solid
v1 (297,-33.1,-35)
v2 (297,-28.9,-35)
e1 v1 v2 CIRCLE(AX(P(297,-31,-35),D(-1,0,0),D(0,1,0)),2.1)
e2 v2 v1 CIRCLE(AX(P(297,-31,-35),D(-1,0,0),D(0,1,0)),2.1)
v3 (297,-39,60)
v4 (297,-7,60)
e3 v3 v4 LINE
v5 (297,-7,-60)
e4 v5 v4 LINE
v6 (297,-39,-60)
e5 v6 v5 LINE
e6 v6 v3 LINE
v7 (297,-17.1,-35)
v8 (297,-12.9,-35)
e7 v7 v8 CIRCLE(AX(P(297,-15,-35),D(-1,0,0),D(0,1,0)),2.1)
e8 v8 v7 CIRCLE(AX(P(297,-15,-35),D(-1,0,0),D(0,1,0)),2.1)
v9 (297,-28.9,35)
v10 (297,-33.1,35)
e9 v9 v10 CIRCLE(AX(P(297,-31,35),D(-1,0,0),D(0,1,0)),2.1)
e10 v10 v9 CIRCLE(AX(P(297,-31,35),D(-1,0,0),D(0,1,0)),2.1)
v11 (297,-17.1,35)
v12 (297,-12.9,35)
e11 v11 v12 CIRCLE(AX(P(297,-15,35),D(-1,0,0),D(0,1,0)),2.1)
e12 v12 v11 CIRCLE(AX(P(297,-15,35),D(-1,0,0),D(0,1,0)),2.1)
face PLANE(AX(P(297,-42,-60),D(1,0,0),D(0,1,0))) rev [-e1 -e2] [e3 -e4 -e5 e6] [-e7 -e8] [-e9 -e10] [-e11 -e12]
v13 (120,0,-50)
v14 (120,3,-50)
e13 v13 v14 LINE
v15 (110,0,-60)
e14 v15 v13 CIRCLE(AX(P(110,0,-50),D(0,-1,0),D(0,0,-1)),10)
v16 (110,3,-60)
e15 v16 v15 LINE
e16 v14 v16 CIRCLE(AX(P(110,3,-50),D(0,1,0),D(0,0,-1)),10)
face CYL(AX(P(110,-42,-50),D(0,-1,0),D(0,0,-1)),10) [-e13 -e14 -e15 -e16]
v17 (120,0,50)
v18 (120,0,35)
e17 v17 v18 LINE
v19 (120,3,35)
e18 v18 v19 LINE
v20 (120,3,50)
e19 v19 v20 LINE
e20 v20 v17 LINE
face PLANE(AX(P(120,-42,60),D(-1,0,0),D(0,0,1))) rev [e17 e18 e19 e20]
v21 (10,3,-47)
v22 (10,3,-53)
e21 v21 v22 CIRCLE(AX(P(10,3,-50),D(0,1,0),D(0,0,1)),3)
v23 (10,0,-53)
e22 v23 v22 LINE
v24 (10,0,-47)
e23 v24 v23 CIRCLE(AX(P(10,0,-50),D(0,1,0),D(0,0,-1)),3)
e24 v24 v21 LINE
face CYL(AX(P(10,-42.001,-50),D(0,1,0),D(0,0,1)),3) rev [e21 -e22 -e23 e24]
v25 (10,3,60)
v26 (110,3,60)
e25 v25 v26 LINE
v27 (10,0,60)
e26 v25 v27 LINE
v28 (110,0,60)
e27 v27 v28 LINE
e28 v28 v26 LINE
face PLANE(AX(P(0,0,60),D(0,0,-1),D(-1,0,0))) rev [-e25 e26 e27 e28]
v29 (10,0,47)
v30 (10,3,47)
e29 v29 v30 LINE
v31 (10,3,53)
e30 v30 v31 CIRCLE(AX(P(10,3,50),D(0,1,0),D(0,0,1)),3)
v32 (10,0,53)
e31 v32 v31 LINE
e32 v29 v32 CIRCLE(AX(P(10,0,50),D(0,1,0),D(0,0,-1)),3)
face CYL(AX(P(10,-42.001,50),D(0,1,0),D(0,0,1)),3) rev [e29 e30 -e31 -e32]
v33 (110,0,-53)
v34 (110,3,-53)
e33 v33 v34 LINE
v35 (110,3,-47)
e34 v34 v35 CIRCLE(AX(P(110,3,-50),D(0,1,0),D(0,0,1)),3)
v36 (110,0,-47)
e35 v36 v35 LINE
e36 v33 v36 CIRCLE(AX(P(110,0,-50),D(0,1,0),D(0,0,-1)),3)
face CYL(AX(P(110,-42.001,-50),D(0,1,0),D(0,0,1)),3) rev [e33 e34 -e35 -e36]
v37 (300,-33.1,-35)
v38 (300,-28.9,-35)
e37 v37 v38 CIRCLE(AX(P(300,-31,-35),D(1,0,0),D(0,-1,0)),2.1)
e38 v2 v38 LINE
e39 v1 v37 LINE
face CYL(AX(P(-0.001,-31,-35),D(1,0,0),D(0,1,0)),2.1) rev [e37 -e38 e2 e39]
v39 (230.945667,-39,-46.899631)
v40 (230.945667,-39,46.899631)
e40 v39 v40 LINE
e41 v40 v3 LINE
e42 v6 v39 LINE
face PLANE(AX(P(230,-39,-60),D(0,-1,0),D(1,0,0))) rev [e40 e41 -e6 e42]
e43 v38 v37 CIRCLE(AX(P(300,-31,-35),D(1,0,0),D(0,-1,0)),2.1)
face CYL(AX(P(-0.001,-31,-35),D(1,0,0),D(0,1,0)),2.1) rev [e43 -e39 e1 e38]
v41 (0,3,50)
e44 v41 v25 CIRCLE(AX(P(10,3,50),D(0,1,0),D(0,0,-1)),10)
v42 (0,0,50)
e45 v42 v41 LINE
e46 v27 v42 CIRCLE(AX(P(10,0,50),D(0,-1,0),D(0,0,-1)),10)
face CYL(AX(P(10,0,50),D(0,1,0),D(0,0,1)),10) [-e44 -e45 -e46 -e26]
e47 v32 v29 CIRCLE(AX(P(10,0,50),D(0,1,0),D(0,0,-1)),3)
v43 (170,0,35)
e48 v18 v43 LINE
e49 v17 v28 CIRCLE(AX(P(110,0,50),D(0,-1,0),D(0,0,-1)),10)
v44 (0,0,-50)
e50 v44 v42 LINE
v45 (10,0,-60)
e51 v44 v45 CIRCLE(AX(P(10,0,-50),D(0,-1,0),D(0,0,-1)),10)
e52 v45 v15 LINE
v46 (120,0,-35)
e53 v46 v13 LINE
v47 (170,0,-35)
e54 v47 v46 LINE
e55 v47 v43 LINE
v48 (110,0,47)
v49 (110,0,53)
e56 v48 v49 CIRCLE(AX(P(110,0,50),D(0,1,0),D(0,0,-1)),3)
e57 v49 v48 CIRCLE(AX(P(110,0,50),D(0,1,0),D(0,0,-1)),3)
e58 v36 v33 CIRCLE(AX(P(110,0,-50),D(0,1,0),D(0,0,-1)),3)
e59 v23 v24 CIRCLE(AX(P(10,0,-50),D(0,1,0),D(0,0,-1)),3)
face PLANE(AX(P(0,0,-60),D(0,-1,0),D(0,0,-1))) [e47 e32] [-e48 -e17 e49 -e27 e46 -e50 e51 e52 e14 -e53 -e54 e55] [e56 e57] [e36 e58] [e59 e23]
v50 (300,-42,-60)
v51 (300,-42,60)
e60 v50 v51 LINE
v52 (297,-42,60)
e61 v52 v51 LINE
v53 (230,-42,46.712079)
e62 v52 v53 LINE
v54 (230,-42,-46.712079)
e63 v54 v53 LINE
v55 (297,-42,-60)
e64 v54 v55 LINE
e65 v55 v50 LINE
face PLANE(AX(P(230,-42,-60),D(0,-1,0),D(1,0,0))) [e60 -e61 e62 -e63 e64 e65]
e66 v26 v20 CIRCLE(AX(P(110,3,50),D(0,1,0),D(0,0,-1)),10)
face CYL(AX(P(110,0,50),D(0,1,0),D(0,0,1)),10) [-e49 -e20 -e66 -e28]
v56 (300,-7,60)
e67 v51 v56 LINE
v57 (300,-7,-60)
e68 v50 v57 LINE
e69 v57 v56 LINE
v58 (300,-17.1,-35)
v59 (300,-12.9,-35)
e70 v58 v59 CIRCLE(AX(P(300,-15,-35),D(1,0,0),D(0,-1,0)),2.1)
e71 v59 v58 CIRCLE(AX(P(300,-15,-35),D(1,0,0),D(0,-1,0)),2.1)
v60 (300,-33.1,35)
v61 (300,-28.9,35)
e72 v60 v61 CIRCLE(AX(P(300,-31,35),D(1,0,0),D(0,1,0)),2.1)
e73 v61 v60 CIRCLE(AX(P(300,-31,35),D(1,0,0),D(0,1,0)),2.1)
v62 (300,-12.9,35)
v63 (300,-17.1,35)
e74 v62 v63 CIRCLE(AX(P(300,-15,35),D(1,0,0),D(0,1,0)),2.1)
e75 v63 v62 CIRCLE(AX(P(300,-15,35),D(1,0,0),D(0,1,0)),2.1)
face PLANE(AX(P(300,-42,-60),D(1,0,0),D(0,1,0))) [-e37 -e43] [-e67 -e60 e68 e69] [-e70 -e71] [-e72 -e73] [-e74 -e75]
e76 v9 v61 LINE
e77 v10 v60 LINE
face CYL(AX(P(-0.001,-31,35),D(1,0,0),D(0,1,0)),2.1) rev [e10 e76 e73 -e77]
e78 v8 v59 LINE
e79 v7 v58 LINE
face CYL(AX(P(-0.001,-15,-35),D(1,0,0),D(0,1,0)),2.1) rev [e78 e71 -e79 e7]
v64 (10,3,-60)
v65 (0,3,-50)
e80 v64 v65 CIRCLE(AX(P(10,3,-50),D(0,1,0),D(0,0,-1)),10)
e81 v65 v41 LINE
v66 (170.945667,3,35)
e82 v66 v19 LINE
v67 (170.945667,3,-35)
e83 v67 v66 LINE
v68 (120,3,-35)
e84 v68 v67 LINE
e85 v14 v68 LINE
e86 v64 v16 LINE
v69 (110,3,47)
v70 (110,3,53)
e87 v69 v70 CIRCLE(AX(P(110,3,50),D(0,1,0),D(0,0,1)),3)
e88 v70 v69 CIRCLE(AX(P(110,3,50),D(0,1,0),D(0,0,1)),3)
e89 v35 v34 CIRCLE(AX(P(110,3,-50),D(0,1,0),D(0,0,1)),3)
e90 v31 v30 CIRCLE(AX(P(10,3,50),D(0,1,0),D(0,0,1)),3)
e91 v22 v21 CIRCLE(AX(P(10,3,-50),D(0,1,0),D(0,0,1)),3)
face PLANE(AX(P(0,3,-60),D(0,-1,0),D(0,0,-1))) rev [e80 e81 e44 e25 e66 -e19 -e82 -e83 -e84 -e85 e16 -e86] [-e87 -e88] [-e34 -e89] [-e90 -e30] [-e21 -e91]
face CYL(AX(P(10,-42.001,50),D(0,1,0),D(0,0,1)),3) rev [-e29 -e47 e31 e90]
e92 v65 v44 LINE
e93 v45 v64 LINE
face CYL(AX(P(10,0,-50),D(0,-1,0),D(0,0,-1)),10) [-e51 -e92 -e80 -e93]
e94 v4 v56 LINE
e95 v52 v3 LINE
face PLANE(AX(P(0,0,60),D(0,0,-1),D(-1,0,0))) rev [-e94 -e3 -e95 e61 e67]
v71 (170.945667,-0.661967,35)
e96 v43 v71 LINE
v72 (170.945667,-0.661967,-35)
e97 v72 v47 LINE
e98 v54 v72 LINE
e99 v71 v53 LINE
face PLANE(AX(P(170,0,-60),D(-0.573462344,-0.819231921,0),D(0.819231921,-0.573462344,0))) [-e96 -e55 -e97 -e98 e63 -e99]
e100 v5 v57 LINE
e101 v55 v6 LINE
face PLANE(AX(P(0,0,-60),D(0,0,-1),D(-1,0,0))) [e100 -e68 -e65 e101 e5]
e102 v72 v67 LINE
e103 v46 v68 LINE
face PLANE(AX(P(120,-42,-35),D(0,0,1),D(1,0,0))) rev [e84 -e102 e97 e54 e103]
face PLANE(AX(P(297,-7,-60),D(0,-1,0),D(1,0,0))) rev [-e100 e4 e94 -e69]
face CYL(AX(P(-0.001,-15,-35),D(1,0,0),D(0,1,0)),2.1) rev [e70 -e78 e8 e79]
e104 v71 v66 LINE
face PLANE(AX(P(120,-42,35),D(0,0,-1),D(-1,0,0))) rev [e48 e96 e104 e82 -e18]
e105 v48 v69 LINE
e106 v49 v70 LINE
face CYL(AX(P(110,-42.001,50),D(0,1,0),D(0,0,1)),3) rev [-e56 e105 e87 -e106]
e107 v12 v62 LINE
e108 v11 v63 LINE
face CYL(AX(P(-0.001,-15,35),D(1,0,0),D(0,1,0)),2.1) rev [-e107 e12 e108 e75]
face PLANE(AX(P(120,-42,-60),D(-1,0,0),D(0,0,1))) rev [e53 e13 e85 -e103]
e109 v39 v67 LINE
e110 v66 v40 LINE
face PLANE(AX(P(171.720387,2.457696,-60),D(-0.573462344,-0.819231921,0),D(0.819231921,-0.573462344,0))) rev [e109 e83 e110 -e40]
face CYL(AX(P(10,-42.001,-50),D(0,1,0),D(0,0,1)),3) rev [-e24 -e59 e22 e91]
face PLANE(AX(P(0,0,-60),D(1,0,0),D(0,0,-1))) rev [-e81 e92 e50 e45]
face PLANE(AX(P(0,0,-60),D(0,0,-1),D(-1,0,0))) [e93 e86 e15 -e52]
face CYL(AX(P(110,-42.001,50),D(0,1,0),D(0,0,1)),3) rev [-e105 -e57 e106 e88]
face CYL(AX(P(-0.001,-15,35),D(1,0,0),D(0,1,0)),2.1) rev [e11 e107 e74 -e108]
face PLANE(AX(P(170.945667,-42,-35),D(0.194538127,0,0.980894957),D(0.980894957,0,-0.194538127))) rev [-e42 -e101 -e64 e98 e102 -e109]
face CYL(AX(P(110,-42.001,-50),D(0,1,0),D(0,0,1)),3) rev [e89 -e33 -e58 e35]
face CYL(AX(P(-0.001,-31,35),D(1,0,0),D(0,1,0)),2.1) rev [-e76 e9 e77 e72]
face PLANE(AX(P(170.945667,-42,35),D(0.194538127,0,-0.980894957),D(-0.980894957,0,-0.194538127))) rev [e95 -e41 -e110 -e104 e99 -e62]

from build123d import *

# Parameters (mm, degrees)
EXTRUDE_1_DEPTH      = 60
EXTRUDE_1_DEPTH_BACK = 60
CUT_EXTRUDE_1_DEPTH  = 310.232921921
FILLET_1_R           = 10
CUT_EXTRUDE_2_REACH  = 311.233
SKETCH_3_R           = 3
CUT_EXTRUDE_3_REACH  = 310.811
SKETCH_4_R           = 2.1


with BuildPart() as part:
    # 草图1 → 拉伸-薄壁1 (new, two sides: drawn at the far end of the back side and taken through both)
    with BuildSketch(Plane.XY.offset(-EXTRUDE_1_DEPTH_BACK)):
        Polygon((0, 0), (170, 0), (230, -42), (300, -42), (300, -7), (297, -7), (297, -39), (230.945666692, -39), (170.945666692, 3), (0, 3), align=None)
    extrude(amount=EXTRUDE_1_DEPTH + EXTRUDE_1_DEPTH_BACK)

    # 草图2 → 切除-拉伸1 (cut, through all)
    with BuildSketch(Plane(origin=(0, 3, 0), x_dir=(1, 0, 0), z_dir=(0, 1, 0))):
        Polygon((120, 60), (120, 35), (170.945666692, 35), (297, 60), align=None)
        Polygon((297, -60), (120, -60), (120, -35), (170.945666692, -35), align=None)
    extrude(amount=-CUT_EXTRUDE_1_DEPTH, mode=Mode.SUBTRACT)

    # 圆角1
    fillet_1_edges = [part.edges().sort_by_distance(p)[0] for p in [
        (0, 1.5, -60),
        (0, 1.5, 60),
        (120, 1.5, -60),
        (120, 1.5, 60),
    ]]
    fillet(fillet_1_edges, radius=FILLET_1_R)

    # 草图3 → 切除-拉伸2 (cut, up to next)
    with BuildSketch(Plane(origin=(0, 3, 0), x_dir=(1, 0, 0), z_dir=(0, 1, 0)), mode=Mode.PRIVATE) as cut_extrude_2_sk1:
        with Locations(Location((10, 50, 0), (0, 0, 270))):
            Circle(SKETCH_3_R)
    cut_extrude_2_tool1 = extrude(cut_extrude_2_sk1.sketch, amount=-CUT_EXTRUDE_2_REACH, mode=Mode.PRIVATE) & part.part
    # 草图3 → 切除-拉伸2 (cut, up to next)
    with BuildSketch(Plane(origin=(0, 3, 0), x_dir=(1, 0, 0), z_dir=(0, 1, 0)), mode=Mode.PRIVATE) as cut_extrude_2_sk2:
        with Locations(Location((110, 50, 0), (0, 0, 270))):
            Circle(SKETCH_3_R)
    cut_extrude_2_tool2 = extrude(cut_extrude_2_sk2.sketch, amount=-CUT_EXTRUDE_2_REACH, mode=Mode.PRIVATE) & part.part
    # 草图3 → 切除-拉伸2 (cut, up to next)
    with BuildSketch(Plane(origin=(0, 3, 0), x_dir=(1, 0, 0), z_dir=(0, 1, 0)), mode=Mode.PRIVATE) as cut_extrude_2_sk3:
        with Locations(Location((110, -50, 0), (0, 0, 270))):
            Circle(SKETCH_3_R)
    cut_extrude_2_tool3 = extrude(cut_extrude_2_sk3.sketch, amount=-CUT_EXTRUDE_2_REACH, mode=Mode.PRIVATE) & part.part
    # 草图3 → 切除-拉伸2 (cut, up to next)
    with BuildSketch(Plane(origin=(0, 3, 0), x_dir=(1, 0, 0), z_dir=(0, 1, 0)), mode=Mode.PRIVATE) as cut_extrude_2_sk4:
        with Locations(Location((10, -50, 0), (0, 0, 270))):
            Circle(SKETCH_3_R)
    cut_extrude_2_tool4 = extrude(cut_extrude_2_sk4.sketch, amount=-CUT_EXTRUDE_2_REACH, mode=Mode.PRIVATE) & part.part
    add(cut_extrude_2_tool1.solids().sort_by_distance((10, 3, -50))[0], mode=Mode.SUBTRACT)
    add(cut_extrude_2_tool2.solids().sort_by_distance((110, 3, -50))[0], mode=Mode.SUBTRACT)
    add(cut_extrude_2_tool3.solids().sort_by_distance((110, 3, 50))[0], mode=Mode.SUBTRACT)
    add(cut_extrude_2_tool4.solids().sort_by_distance((10, 3, 50))[0], mode=Mode.SUBTRACT)

    # 草图4 → 切除-拉伸3 (cut, up to next)
    with BuildSketch(Plane(origin=(300, 0, 0), x_dir=(0, 0, -1), z_dir=(1, 0, 0)), mode=Mode.PRIVATE) as cut_extrude_3_sk1:
        with Locations(Location((-35, -15, 0), (0, 0, 90))):
            Circle(SKETCH_4_R)
    cut_extrude_3_tool1 = extrude(cut_extrude_3_sk1.sketch, amount=-CUT_EXTRUDE_3_REACH, mode=Mode.PRIVATE) & part.part
    # 草图4 → 切除-拉伸3 (cut, up to next)
    with BuildSketch(Plane(origin=(300, 0, 0), x_dir=(0, 0, -1), z_dir=(1, 0, 0)), mode=Mode.PRIVATE) as cut_extrude_3_sk2:
        with Locations(Location((-35, -31, 0), (0, 0, 90))):
            Circle(SKETCH_4_R)
    cut_extrude_3_tool2 = extrude(cut_extrude_3_sk2.sketch, amount=-CUT_EXTRUDE_3_REACH, mode=Mode.PRIVATE) & part.part
    # 草图4 → 切除-拉伸3 (cut, up to next)
    with BuildSketch(Plane(origin=(300, 0, 0), x_dir=(0, 0, -1), z_dir=(1, 0, 0)), mode=Mode.PRIVATE) as cut_extrude_3_sk3:
        with Locations(Location((35, -31, 0), (0, 0, 90))):
            Circle(SKETCH_4_R)
    cut_extrude_3_tool3 = extrude(cut_extrude_3_sk3.sketch, amount=-CUT_EXTRUDE_3_REACH, mode=Mode.PRIVATE) & part.part
    # 草图4 → 切除-拉伸3 (cut, up to next)
    with BuildSketch(Plane(origin=(300, 0, 0), x_dir=(0, 0, -1), z_dir=(1, 0, 0)), mode=Mode.PRIVATE) as cut_extrude_3_sk4:
        with Locations(Location((35, -15, 0), (0, 0, 90))):
            Circle(SKETCH_4_R)
    cut_extrude_3_tool4 = extrude(cut_extrude_3_sk4.sketch, amount=-CUT_EXTRUDE_3_REACH, mode=Mode.PRIVATE) & part.part
    add(cut_extrude_3_tool1.solids().sort_by_distance((300, -15, 35))[0], mode=Mode.SUBTRACT)
    add(cut_extrude_3_tool2.solids().sort_by_distance((300, -31, 35))[0], mode=Mode.SUBTRACT)
    add(cut_extrude_3_tool3.solids().sort_by_distance((300, -31, -35))[0], mode=Mode.SUBTRACT)
    add(cut_extrude_3_tool4.solids().sort_by_distance((300, -15, -35))[0], mode=Mode.SUBTRACT)


solid = part.part
